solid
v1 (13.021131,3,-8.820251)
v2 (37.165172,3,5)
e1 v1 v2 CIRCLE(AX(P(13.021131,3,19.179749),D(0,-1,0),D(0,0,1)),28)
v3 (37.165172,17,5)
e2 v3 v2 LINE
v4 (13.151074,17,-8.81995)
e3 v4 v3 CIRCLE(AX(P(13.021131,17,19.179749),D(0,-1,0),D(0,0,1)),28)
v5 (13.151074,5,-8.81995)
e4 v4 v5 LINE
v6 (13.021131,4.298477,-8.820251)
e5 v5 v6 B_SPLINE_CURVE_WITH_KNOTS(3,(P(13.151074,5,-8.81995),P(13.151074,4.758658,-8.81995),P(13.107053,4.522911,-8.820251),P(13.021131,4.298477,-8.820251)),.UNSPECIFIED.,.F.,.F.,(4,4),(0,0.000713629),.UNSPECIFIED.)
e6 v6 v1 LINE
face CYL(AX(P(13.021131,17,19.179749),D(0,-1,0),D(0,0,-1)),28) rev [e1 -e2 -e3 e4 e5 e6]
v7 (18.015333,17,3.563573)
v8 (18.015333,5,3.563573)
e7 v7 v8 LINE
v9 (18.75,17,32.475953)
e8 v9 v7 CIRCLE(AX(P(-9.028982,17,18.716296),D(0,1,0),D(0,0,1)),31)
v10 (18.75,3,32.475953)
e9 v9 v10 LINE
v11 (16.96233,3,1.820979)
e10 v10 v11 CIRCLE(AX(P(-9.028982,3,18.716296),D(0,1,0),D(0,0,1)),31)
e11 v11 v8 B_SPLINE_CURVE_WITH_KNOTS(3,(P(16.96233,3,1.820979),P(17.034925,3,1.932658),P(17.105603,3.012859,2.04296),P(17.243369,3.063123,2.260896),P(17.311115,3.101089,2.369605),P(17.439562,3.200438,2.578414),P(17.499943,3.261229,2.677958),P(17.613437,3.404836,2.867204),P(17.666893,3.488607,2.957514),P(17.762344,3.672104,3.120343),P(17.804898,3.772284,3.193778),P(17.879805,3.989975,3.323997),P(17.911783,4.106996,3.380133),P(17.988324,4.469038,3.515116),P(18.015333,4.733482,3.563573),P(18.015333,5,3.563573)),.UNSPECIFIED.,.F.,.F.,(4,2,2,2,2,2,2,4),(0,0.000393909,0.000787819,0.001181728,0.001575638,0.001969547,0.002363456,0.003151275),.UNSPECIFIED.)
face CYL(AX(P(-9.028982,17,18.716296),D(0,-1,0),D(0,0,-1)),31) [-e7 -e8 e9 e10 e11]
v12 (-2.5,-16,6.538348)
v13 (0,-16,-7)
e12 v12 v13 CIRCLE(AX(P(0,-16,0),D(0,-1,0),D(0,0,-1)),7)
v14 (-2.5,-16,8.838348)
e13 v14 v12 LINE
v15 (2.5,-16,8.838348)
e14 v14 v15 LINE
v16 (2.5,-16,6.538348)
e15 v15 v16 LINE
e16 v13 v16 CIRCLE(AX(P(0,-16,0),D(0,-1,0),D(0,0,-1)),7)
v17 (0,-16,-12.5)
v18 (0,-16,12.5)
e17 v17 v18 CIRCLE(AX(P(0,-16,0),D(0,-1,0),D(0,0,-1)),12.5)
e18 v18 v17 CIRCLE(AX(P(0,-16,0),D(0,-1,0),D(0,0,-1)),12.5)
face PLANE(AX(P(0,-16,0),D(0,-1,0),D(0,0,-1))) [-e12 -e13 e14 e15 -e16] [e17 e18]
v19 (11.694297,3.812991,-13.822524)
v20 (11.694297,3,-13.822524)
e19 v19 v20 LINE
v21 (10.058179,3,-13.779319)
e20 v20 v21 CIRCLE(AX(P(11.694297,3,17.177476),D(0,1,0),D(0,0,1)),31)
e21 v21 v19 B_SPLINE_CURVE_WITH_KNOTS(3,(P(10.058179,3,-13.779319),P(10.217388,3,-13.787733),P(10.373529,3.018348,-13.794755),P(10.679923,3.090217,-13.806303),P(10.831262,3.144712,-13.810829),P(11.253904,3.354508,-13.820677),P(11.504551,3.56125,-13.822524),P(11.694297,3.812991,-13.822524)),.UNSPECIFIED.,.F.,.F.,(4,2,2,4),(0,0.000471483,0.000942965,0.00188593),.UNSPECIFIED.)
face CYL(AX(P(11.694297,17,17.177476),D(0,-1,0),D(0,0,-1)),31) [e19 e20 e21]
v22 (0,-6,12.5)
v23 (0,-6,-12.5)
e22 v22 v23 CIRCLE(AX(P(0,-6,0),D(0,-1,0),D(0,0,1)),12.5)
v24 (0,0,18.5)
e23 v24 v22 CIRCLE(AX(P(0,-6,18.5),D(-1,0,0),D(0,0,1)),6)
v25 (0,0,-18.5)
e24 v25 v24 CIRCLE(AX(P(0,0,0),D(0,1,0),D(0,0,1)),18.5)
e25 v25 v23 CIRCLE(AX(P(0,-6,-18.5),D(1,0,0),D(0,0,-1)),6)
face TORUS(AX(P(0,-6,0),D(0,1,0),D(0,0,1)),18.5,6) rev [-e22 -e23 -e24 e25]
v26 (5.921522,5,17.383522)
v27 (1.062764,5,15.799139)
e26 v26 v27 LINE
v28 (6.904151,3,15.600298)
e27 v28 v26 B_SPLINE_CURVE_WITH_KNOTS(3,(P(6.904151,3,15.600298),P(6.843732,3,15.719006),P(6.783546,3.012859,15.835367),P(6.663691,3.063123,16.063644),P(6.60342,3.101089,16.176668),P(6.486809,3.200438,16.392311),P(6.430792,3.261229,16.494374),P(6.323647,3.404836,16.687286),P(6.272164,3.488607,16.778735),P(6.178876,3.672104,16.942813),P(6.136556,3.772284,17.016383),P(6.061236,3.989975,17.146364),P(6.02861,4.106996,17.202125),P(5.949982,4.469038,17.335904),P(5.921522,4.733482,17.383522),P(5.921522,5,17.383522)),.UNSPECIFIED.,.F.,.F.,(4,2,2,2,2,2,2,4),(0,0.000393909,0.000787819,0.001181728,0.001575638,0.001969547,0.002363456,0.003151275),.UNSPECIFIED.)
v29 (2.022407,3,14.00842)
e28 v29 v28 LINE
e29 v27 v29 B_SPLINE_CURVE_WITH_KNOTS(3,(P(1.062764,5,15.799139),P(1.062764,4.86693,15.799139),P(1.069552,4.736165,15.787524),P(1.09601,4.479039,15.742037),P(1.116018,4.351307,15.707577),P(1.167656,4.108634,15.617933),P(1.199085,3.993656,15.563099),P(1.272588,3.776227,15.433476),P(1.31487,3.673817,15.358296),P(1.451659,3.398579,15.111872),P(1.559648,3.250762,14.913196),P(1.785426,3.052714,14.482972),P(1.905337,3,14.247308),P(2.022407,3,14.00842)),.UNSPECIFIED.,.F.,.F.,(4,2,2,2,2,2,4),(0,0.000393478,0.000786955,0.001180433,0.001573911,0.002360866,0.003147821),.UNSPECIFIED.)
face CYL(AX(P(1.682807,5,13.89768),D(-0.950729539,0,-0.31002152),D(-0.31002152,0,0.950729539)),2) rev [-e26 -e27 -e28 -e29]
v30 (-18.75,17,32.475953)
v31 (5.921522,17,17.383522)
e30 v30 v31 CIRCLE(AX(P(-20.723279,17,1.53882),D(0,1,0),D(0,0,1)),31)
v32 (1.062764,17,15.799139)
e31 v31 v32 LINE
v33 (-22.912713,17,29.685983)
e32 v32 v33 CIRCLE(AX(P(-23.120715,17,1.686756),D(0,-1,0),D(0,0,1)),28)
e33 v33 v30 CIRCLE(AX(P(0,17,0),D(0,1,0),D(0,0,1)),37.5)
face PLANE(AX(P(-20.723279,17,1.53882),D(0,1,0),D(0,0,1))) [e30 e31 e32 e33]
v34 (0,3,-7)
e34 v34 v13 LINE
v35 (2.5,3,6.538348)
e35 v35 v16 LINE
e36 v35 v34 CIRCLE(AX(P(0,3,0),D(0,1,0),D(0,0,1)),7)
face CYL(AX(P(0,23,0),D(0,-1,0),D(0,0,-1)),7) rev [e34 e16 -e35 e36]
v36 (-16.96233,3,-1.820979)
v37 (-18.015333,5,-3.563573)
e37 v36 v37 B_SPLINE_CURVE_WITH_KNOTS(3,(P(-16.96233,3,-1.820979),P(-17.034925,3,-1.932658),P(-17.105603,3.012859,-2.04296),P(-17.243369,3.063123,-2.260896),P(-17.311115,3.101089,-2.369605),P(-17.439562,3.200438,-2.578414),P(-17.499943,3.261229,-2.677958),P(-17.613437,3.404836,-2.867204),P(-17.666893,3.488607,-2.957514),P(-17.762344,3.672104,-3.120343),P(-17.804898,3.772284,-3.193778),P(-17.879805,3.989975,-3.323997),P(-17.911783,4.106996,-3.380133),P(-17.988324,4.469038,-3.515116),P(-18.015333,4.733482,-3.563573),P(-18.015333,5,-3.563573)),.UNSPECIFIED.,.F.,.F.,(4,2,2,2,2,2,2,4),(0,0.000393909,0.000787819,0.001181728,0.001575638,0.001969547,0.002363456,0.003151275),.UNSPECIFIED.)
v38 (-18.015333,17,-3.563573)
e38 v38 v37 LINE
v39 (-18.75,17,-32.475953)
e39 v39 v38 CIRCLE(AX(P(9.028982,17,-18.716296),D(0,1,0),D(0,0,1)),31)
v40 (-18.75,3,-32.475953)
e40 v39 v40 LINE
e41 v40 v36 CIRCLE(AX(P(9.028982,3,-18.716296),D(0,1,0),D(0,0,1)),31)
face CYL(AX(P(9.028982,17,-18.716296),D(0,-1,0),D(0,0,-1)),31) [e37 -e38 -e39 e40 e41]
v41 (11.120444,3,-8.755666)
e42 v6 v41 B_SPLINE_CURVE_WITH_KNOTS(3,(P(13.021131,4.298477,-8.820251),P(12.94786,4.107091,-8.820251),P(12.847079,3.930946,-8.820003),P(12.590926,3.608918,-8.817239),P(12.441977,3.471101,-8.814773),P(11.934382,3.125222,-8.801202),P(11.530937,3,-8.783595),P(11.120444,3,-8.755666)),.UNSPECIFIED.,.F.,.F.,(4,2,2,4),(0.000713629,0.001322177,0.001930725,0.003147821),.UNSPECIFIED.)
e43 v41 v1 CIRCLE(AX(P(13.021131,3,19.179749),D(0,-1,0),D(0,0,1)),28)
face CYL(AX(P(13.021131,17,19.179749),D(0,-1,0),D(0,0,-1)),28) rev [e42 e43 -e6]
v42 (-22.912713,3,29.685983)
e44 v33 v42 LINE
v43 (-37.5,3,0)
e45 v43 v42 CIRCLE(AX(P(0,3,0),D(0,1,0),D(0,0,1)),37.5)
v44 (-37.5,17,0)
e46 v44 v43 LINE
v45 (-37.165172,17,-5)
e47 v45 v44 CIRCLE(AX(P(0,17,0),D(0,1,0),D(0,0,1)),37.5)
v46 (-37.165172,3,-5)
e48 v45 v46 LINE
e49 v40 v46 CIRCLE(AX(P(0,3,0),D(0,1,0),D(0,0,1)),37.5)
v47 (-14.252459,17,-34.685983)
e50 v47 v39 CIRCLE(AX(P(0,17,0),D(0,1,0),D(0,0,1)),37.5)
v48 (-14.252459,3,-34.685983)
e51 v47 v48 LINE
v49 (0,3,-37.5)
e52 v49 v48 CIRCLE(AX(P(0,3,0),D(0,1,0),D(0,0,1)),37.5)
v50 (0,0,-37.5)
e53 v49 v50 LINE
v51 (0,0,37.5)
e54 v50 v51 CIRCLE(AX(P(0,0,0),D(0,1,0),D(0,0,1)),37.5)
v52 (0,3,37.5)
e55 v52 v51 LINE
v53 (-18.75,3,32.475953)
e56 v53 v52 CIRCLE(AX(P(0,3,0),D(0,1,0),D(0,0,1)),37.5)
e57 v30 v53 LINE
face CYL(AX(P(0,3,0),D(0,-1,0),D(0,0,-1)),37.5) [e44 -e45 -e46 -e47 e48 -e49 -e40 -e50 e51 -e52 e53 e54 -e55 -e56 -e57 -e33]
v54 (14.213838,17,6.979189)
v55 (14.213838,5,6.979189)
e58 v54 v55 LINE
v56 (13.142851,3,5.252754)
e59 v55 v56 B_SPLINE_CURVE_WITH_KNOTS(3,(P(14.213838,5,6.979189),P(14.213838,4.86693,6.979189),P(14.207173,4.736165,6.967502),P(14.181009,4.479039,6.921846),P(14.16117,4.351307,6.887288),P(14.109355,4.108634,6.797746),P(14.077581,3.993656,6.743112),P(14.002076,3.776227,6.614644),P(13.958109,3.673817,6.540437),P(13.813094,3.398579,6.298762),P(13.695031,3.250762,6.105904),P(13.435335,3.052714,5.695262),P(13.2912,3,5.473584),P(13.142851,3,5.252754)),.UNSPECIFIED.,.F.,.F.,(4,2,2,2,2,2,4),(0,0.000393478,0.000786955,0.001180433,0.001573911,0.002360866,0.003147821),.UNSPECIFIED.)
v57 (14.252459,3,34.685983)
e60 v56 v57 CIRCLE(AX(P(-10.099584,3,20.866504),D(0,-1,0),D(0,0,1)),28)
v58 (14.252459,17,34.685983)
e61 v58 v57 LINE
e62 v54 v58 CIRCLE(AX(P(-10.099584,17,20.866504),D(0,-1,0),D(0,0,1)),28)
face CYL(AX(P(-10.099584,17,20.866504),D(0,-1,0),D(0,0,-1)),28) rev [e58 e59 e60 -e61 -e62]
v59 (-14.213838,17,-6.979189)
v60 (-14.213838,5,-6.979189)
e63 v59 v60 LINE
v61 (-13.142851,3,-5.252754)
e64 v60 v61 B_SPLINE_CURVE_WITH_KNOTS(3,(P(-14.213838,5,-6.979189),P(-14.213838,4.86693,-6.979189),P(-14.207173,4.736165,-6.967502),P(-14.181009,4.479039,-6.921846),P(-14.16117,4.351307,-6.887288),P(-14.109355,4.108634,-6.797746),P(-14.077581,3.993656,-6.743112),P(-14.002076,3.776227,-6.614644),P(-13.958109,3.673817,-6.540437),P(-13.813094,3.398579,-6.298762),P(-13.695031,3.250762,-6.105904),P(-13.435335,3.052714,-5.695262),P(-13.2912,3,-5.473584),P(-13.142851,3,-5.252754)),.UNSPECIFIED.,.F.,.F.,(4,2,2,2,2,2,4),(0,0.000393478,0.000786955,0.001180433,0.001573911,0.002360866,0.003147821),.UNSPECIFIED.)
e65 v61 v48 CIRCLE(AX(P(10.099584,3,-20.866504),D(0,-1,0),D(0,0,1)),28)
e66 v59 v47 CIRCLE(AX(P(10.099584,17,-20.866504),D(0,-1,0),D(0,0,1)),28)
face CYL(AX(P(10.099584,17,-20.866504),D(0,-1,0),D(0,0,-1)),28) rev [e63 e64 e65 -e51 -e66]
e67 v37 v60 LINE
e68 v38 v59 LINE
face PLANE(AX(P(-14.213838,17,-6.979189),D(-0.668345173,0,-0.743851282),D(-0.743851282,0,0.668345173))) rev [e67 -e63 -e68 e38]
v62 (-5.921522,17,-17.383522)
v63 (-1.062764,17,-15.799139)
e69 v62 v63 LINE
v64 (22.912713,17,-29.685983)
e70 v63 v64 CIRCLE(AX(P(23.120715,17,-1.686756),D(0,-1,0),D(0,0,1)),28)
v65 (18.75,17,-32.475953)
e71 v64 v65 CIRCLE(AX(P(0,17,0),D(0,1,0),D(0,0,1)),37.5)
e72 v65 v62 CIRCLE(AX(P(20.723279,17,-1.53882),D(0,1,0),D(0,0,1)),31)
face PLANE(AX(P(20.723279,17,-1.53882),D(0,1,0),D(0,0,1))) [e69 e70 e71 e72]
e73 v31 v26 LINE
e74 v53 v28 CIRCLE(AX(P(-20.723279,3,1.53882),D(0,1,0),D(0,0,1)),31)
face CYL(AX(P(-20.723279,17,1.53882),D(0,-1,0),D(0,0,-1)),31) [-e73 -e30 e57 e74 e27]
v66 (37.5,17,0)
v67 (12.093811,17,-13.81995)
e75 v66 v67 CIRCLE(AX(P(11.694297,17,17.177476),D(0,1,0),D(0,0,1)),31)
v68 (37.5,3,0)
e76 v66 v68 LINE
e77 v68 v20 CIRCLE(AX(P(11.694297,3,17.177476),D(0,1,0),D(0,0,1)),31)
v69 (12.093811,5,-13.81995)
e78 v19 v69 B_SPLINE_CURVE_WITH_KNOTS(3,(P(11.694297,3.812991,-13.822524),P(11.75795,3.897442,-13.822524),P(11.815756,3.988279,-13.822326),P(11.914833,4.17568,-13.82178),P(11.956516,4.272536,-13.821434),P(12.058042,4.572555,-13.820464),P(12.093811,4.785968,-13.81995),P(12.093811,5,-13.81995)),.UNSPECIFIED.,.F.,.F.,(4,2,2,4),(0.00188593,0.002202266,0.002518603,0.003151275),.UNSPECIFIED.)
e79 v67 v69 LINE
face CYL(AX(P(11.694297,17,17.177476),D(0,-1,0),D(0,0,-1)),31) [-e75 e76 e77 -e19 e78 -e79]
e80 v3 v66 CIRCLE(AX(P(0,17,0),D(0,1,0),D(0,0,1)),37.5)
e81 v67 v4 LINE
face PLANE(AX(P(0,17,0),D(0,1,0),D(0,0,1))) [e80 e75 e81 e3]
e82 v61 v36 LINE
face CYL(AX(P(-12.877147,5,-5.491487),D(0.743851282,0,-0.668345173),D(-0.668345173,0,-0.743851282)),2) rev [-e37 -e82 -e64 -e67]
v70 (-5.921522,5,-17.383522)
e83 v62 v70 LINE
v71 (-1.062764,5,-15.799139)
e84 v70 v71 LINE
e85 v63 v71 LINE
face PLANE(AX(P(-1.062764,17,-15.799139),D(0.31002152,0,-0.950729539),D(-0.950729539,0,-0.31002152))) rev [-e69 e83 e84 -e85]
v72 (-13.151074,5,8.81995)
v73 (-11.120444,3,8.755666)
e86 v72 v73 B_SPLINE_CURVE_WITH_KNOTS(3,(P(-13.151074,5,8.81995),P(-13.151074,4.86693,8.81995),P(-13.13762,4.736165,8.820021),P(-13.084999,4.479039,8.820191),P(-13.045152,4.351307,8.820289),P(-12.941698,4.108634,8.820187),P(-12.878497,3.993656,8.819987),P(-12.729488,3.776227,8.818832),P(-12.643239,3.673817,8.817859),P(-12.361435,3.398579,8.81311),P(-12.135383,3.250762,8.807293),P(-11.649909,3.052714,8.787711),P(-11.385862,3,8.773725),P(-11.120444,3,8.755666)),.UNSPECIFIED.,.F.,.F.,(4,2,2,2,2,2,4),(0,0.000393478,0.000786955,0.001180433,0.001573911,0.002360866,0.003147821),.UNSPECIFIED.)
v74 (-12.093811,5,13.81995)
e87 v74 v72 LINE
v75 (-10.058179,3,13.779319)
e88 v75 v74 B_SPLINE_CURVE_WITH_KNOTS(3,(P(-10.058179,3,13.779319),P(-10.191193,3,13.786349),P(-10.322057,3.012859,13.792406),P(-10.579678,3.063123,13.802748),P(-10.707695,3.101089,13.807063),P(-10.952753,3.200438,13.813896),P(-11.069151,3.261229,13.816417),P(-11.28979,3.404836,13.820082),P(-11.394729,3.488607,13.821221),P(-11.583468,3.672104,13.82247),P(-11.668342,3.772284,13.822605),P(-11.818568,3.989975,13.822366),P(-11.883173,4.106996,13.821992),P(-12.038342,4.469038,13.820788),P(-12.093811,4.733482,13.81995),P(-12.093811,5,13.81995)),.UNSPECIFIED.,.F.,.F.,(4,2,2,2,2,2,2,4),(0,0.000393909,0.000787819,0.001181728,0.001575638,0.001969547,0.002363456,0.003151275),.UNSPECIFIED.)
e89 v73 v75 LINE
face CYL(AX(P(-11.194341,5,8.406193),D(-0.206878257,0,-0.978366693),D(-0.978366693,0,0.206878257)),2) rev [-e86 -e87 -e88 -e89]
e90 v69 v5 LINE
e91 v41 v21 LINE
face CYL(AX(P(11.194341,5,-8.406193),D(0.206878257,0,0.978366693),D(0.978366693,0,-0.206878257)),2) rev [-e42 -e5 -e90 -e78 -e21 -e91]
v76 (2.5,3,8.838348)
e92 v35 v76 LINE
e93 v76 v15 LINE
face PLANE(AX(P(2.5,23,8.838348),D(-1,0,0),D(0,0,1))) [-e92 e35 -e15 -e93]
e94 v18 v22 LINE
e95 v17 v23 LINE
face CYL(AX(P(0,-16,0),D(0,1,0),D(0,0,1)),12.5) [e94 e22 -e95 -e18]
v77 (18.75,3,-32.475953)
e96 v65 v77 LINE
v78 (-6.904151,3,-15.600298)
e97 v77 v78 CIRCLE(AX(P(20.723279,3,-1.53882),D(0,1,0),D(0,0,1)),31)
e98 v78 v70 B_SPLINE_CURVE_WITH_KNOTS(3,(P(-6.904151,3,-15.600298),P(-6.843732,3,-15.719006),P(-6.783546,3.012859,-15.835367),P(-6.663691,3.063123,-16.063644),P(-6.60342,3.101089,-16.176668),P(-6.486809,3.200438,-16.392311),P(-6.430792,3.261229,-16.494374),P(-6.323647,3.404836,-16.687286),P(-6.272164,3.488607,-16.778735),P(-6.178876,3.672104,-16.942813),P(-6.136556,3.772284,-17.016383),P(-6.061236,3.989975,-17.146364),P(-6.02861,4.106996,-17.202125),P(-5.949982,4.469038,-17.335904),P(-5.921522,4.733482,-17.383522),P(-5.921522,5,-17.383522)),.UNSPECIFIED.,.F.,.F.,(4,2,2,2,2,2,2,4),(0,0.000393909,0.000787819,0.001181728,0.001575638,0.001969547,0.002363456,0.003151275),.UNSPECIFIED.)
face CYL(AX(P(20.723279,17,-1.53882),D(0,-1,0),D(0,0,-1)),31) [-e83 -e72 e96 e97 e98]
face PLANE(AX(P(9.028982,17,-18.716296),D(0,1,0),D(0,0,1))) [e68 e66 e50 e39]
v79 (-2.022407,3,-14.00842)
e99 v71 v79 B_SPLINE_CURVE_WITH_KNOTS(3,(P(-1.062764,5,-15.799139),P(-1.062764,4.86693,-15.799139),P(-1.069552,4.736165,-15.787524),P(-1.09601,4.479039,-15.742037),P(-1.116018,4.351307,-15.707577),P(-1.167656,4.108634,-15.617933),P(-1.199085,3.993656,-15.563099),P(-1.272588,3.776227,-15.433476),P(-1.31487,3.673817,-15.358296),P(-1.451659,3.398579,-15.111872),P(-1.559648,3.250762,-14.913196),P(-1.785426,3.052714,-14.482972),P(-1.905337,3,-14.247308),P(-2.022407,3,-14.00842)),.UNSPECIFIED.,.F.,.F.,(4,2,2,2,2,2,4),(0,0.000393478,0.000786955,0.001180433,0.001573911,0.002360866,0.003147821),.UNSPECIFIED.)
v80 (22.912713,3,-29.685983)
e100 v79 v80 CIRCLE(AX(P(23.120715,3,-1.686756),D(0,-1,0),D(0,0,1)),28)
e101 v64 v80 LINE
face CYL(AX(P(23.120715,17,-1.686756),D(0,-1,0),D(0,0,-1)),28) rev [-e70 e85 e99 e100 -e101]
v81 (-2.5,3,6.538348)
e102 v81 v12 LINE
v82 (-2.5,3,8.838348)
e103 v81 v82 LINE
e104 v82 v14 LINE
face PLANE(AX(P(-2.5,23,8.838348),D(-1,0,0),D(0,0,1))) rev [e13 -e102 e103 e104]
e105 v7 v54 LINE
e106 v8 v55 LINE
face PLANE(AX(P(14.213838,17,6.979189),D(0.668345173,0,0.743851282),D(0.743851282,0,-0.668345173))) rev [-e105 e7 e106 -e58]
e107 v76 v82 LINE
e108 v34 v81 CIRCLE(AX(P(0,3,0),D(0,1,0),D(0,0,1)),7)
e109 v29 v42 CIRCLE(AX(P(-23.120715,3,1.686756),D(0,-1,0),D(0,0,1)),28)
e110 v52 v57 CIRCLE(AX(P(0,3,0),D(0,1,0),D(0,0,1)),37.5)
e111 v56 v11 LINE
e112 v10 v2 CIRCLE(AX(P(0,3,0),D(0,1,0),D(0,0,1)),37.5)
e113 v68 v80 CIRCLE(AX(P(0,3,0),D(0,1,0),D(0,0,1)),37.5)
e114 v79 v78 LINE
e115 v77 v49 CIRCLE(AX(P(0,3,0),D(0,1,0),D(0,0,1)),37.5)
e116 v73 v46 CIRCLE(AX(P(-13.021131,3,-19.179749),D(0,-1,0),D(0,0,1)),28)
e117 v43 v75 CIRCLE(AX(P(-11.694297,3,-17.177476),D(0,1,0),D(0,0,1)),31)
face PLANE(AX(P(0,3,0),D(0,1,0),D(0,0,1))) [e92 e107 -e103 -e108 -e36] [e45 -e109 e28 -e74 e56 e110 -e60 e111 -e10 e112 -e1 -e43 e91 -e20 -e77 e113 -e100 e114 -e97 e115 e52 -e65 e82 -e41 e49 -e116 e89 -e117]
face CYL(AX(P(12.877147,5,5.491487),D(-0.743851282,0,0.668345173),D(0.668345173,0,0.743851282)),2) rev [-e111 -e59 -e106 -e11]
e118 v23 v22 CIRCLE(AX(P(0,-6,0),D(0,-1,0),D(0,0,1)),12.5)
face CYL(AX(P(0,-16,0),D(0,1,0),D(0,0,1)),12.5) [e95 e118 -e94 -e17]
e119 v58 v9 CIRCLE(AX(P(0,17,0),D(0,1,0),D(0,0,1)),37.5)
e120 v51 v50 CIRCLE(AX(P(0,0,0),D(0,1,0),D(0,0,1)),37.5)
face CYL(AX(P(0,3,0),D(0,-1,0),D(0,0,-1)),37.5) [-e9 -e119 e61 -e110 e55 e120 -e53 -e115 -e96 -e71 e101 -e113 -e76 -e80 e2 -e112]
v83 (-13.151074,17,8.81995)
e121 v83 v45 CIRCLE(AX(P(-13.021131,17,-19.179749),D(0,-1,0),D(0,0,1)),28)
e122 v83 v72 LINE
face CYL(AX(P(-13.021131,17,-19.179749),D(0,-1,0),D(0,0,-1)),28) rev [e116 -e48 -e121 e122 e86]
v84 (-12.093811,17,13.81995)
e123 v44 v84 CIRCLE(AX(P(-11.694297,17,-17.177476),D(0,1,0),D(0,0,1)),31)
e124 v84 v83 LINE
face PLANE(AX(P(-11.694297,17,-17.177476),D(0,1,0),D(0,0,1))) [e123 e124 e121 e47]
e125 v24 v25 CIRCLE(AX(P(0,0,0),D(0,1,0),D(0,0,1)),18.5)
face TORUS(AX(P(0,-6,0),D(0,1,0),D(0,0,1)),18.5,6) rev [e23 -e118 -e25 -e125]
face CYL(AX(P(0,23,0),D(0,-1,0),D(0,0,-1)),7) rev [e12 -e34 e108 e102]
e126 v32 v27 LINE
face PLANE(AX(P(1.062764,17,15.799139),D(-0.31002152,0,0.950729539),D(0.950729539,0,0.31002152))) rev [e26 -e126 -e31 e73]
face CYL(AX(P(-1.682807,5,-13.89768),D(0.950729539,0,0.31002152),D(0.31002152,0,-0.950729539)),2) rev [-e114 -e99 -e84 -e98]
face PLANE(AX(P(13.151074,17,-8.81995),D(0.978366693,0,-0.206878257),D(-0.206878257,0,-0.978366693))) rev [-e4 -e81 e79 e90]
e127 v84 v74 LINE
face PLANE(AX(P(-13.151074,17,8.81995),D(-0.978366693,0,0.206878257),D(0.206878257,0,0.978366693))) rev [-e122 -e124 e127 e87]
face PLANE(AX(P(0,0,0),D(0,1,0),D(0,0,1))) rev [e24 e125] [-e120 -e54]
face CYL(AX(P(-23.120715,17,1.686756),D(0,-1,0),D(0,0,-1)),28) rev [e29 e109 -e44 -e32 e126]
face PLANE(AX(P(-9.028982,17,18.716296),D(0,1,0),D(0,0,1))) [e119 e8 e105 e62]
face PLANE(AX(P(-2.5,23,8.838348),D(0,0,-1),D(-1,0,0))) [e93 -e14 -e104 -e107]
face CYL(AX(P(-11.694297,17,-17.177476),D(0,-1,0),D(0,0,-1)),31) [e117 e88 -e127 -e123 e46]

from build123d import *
from build123d.topology import SkipClean

# Parameters (mm, degrees)
BASE_DISC_SKETCH_75_R = 37.5
BASE_DISC_75X3_DEPTH  = 3
HUB_AND_BORE_SKETCH_R = 12.5
HUB_BOSS_DEPTH        = 16
SHAFT_BORE_DEPTH      = 23
HUB_FILLET_R6_R       = 6
VANES_6X_DEPTH        = 14
VANE_FILLETS_R2_R     = 2


with BuildPart() as part:
    # Base Disc Sketch _75 → Base Disc _75x3 (new body)
    with BuildSketch(Plane(origin=(0, 0, 0), x_dir=(1, 0, 0), z_dir=(0, 1, 0))):
        with Locations(Location((0, 0, 0), (0, 0, 270))):
            Circle(BASE_DISC_SKETCH_75_R)
    extrude(amount=BASE_DISC_75X3_DEPTH)

    # Hub and Bore Sketch → Hub Boss (add)
    with BuildSketch(Plane.XZ):
        with Locations(Location((0, 0, 0), (0, 0, 270))):
            Circle(HUB_AND_BORE_SKETCH_R)
    extrude(amount=HUB_BOSS_DEPTH)

    # Sketch2_3 → Shaft Bore (cut, symmetric)
    with BuildSketch(Plane.XZ):
        with BuildLine():
            Line((-2.5, 8.838348415), (2.5, 8.838348415))
            Line((2.5, 8.838348415), (2.5, 6.538348415))
            ThreePointArc((2.5, 6.538348415), (0, -7), (-2.5, 6.538348415))
            Line((-2.5, 6.538348415), (-2.5, 8.838348415))
        make_face()
    extrude(amount=SHAFT_BORE_DEPTH, both=True, mode=Mode.SUBTRACT)

    # Hub Fillet R6
    hub_fillet_r6_edges = [part.edges().sort_by_distance(p)[0] for p in [
        (0, 0, 12.5),
    ]]
    fillet(hub_fillet_r6_edges, radius=HUB_FILLET_R6_R)

    # Vane Profiles Sketch 6x → Vanes 6x (add)
    with SkipClean():  # the faces are left unmerged after this step: merging them gives an invalid solid
        with BuildSketch(Plane(origin=(0, 3, 0), x_dir=(1, 0, 0), z_dir=(0, 1, 0))):
            with BuildLine():
                Line((13.151074283, 8.81994991), (12.093810893, 13.81994991))
                ThreePointArc((12.093810893, 13.81994991), (26.507335187, 10.054378643), (37.5, 0))
                ThreePointArc((37.5, 0), (37.416199333, -2.505599224), (37.165171868, -5))
                ThreePointArc((37.165171868, -5), (26.987316196, 5.088454065), (13.151074283, 8.81994991))
            make_face()
            with BuildLine():
                Line((14.213837824, -6.979189461), (18.015333148, -3.563572506))
                ThreePointArc((18.015333148, -3.563572506), (21.961014917, -17.928836338), (18.75, -32.475952642))
                ThreePointArc((18.75, -32.475952642), (16.538187087, -33.656178747), (14.252458915, -34.685982974))
                ThreePointArc((14.252458915, -34.685982974), (17.900388584, -20.827474373), (14.213837824, -6.979189461))
            make_face()
            with BuildLine():
                Line((1.062763541, -15.799139371), (5.921522255, -17.383522417))
                ThreePointArc((5.921522255, -17.383522417), (-4.54632027, -27.98321498), (-18.75, -32.475952642))
                ThreePointArc((-18.75, -32.475952642), (-20.878012246, -31.150579524), (-22.912712953, -29.685982974))
                ThreePointArc((-22.912712953, -29.685982974), (-9.086927612, -25.915928438), (1.062763541, -15.799139371))
            make_face()
            with BuildLine():
                Line((-13.151074283, -8.81994991), (-12.093810893, -13.81994991))
                ThreePointArc((-12.093810893, -13.81994991), (-26.507335187, -10.054378643), (-37.5, 0))
                ThreePointArc((-37.5, 0), (-37.416199333, 2.505599224), (-37.165171868, 5))
                ThreePointArc((-37.165171868, 5), (-26.987316196, -5.088454065), (-13.151074283, -8.81994991))
            make_face()
            with BuildLine():
                Line((-14.213837824, 6.979189461), (-18.015333148, 3.563572506))
                ThreePointArc((-18.015333148, 3.563572506), (-21.961014917, 17.928836338), (-18.75, 32.475952642))
                ThreePointArc((-18.75, 32.475952642), (-16.538187087, 33.656178747), (-14.252458915, 34.685982974))
                ThreePointArc((-14.252458915, 34.685982974), (-17.900388584, 20.827474373), (-14.213837824, 6.979189461))
            make_face()
            with BuildLine():
                Line((-1.062763541, 15.799139371), (-5.921522255, 17.383522417))
                ThreePointArc((-5.921522255, 17.383522417), (4.54632027, 27.98321498), (18.75, 32.475952642))
                ThreePointArc((18.75, 32.475952642), (20.878012246, 31.150579524), (22.912712953, 29.685982974))
                ThreePointArc((22.912712953, 29.685982974), (9.086927612, 25.915928438), (-1.062763541, 15.799139371))
            make_face()
        extrude(amount=VANES_6X_DEPTH)

    # Vane Fillets R2
    vane_fillets_r2_edges = [part.edges().sort_by_distance(p)[0] for p in [
        (12.622442588, 3, -11.31994991),
        (16.114585486, 3, 5.271380984),
        (3.492142898, 3, 16.591330894),
        (-12.622442588, 3, 11.31994991),
        (-16.114585486, 3, -5.271380984),
        (-3.492142898, 3, -16.591330894),
    ]]
    fillet(vane_fillets_r2_edges, radius=VANE_FILLETS_R2_R)


solid = part.part
